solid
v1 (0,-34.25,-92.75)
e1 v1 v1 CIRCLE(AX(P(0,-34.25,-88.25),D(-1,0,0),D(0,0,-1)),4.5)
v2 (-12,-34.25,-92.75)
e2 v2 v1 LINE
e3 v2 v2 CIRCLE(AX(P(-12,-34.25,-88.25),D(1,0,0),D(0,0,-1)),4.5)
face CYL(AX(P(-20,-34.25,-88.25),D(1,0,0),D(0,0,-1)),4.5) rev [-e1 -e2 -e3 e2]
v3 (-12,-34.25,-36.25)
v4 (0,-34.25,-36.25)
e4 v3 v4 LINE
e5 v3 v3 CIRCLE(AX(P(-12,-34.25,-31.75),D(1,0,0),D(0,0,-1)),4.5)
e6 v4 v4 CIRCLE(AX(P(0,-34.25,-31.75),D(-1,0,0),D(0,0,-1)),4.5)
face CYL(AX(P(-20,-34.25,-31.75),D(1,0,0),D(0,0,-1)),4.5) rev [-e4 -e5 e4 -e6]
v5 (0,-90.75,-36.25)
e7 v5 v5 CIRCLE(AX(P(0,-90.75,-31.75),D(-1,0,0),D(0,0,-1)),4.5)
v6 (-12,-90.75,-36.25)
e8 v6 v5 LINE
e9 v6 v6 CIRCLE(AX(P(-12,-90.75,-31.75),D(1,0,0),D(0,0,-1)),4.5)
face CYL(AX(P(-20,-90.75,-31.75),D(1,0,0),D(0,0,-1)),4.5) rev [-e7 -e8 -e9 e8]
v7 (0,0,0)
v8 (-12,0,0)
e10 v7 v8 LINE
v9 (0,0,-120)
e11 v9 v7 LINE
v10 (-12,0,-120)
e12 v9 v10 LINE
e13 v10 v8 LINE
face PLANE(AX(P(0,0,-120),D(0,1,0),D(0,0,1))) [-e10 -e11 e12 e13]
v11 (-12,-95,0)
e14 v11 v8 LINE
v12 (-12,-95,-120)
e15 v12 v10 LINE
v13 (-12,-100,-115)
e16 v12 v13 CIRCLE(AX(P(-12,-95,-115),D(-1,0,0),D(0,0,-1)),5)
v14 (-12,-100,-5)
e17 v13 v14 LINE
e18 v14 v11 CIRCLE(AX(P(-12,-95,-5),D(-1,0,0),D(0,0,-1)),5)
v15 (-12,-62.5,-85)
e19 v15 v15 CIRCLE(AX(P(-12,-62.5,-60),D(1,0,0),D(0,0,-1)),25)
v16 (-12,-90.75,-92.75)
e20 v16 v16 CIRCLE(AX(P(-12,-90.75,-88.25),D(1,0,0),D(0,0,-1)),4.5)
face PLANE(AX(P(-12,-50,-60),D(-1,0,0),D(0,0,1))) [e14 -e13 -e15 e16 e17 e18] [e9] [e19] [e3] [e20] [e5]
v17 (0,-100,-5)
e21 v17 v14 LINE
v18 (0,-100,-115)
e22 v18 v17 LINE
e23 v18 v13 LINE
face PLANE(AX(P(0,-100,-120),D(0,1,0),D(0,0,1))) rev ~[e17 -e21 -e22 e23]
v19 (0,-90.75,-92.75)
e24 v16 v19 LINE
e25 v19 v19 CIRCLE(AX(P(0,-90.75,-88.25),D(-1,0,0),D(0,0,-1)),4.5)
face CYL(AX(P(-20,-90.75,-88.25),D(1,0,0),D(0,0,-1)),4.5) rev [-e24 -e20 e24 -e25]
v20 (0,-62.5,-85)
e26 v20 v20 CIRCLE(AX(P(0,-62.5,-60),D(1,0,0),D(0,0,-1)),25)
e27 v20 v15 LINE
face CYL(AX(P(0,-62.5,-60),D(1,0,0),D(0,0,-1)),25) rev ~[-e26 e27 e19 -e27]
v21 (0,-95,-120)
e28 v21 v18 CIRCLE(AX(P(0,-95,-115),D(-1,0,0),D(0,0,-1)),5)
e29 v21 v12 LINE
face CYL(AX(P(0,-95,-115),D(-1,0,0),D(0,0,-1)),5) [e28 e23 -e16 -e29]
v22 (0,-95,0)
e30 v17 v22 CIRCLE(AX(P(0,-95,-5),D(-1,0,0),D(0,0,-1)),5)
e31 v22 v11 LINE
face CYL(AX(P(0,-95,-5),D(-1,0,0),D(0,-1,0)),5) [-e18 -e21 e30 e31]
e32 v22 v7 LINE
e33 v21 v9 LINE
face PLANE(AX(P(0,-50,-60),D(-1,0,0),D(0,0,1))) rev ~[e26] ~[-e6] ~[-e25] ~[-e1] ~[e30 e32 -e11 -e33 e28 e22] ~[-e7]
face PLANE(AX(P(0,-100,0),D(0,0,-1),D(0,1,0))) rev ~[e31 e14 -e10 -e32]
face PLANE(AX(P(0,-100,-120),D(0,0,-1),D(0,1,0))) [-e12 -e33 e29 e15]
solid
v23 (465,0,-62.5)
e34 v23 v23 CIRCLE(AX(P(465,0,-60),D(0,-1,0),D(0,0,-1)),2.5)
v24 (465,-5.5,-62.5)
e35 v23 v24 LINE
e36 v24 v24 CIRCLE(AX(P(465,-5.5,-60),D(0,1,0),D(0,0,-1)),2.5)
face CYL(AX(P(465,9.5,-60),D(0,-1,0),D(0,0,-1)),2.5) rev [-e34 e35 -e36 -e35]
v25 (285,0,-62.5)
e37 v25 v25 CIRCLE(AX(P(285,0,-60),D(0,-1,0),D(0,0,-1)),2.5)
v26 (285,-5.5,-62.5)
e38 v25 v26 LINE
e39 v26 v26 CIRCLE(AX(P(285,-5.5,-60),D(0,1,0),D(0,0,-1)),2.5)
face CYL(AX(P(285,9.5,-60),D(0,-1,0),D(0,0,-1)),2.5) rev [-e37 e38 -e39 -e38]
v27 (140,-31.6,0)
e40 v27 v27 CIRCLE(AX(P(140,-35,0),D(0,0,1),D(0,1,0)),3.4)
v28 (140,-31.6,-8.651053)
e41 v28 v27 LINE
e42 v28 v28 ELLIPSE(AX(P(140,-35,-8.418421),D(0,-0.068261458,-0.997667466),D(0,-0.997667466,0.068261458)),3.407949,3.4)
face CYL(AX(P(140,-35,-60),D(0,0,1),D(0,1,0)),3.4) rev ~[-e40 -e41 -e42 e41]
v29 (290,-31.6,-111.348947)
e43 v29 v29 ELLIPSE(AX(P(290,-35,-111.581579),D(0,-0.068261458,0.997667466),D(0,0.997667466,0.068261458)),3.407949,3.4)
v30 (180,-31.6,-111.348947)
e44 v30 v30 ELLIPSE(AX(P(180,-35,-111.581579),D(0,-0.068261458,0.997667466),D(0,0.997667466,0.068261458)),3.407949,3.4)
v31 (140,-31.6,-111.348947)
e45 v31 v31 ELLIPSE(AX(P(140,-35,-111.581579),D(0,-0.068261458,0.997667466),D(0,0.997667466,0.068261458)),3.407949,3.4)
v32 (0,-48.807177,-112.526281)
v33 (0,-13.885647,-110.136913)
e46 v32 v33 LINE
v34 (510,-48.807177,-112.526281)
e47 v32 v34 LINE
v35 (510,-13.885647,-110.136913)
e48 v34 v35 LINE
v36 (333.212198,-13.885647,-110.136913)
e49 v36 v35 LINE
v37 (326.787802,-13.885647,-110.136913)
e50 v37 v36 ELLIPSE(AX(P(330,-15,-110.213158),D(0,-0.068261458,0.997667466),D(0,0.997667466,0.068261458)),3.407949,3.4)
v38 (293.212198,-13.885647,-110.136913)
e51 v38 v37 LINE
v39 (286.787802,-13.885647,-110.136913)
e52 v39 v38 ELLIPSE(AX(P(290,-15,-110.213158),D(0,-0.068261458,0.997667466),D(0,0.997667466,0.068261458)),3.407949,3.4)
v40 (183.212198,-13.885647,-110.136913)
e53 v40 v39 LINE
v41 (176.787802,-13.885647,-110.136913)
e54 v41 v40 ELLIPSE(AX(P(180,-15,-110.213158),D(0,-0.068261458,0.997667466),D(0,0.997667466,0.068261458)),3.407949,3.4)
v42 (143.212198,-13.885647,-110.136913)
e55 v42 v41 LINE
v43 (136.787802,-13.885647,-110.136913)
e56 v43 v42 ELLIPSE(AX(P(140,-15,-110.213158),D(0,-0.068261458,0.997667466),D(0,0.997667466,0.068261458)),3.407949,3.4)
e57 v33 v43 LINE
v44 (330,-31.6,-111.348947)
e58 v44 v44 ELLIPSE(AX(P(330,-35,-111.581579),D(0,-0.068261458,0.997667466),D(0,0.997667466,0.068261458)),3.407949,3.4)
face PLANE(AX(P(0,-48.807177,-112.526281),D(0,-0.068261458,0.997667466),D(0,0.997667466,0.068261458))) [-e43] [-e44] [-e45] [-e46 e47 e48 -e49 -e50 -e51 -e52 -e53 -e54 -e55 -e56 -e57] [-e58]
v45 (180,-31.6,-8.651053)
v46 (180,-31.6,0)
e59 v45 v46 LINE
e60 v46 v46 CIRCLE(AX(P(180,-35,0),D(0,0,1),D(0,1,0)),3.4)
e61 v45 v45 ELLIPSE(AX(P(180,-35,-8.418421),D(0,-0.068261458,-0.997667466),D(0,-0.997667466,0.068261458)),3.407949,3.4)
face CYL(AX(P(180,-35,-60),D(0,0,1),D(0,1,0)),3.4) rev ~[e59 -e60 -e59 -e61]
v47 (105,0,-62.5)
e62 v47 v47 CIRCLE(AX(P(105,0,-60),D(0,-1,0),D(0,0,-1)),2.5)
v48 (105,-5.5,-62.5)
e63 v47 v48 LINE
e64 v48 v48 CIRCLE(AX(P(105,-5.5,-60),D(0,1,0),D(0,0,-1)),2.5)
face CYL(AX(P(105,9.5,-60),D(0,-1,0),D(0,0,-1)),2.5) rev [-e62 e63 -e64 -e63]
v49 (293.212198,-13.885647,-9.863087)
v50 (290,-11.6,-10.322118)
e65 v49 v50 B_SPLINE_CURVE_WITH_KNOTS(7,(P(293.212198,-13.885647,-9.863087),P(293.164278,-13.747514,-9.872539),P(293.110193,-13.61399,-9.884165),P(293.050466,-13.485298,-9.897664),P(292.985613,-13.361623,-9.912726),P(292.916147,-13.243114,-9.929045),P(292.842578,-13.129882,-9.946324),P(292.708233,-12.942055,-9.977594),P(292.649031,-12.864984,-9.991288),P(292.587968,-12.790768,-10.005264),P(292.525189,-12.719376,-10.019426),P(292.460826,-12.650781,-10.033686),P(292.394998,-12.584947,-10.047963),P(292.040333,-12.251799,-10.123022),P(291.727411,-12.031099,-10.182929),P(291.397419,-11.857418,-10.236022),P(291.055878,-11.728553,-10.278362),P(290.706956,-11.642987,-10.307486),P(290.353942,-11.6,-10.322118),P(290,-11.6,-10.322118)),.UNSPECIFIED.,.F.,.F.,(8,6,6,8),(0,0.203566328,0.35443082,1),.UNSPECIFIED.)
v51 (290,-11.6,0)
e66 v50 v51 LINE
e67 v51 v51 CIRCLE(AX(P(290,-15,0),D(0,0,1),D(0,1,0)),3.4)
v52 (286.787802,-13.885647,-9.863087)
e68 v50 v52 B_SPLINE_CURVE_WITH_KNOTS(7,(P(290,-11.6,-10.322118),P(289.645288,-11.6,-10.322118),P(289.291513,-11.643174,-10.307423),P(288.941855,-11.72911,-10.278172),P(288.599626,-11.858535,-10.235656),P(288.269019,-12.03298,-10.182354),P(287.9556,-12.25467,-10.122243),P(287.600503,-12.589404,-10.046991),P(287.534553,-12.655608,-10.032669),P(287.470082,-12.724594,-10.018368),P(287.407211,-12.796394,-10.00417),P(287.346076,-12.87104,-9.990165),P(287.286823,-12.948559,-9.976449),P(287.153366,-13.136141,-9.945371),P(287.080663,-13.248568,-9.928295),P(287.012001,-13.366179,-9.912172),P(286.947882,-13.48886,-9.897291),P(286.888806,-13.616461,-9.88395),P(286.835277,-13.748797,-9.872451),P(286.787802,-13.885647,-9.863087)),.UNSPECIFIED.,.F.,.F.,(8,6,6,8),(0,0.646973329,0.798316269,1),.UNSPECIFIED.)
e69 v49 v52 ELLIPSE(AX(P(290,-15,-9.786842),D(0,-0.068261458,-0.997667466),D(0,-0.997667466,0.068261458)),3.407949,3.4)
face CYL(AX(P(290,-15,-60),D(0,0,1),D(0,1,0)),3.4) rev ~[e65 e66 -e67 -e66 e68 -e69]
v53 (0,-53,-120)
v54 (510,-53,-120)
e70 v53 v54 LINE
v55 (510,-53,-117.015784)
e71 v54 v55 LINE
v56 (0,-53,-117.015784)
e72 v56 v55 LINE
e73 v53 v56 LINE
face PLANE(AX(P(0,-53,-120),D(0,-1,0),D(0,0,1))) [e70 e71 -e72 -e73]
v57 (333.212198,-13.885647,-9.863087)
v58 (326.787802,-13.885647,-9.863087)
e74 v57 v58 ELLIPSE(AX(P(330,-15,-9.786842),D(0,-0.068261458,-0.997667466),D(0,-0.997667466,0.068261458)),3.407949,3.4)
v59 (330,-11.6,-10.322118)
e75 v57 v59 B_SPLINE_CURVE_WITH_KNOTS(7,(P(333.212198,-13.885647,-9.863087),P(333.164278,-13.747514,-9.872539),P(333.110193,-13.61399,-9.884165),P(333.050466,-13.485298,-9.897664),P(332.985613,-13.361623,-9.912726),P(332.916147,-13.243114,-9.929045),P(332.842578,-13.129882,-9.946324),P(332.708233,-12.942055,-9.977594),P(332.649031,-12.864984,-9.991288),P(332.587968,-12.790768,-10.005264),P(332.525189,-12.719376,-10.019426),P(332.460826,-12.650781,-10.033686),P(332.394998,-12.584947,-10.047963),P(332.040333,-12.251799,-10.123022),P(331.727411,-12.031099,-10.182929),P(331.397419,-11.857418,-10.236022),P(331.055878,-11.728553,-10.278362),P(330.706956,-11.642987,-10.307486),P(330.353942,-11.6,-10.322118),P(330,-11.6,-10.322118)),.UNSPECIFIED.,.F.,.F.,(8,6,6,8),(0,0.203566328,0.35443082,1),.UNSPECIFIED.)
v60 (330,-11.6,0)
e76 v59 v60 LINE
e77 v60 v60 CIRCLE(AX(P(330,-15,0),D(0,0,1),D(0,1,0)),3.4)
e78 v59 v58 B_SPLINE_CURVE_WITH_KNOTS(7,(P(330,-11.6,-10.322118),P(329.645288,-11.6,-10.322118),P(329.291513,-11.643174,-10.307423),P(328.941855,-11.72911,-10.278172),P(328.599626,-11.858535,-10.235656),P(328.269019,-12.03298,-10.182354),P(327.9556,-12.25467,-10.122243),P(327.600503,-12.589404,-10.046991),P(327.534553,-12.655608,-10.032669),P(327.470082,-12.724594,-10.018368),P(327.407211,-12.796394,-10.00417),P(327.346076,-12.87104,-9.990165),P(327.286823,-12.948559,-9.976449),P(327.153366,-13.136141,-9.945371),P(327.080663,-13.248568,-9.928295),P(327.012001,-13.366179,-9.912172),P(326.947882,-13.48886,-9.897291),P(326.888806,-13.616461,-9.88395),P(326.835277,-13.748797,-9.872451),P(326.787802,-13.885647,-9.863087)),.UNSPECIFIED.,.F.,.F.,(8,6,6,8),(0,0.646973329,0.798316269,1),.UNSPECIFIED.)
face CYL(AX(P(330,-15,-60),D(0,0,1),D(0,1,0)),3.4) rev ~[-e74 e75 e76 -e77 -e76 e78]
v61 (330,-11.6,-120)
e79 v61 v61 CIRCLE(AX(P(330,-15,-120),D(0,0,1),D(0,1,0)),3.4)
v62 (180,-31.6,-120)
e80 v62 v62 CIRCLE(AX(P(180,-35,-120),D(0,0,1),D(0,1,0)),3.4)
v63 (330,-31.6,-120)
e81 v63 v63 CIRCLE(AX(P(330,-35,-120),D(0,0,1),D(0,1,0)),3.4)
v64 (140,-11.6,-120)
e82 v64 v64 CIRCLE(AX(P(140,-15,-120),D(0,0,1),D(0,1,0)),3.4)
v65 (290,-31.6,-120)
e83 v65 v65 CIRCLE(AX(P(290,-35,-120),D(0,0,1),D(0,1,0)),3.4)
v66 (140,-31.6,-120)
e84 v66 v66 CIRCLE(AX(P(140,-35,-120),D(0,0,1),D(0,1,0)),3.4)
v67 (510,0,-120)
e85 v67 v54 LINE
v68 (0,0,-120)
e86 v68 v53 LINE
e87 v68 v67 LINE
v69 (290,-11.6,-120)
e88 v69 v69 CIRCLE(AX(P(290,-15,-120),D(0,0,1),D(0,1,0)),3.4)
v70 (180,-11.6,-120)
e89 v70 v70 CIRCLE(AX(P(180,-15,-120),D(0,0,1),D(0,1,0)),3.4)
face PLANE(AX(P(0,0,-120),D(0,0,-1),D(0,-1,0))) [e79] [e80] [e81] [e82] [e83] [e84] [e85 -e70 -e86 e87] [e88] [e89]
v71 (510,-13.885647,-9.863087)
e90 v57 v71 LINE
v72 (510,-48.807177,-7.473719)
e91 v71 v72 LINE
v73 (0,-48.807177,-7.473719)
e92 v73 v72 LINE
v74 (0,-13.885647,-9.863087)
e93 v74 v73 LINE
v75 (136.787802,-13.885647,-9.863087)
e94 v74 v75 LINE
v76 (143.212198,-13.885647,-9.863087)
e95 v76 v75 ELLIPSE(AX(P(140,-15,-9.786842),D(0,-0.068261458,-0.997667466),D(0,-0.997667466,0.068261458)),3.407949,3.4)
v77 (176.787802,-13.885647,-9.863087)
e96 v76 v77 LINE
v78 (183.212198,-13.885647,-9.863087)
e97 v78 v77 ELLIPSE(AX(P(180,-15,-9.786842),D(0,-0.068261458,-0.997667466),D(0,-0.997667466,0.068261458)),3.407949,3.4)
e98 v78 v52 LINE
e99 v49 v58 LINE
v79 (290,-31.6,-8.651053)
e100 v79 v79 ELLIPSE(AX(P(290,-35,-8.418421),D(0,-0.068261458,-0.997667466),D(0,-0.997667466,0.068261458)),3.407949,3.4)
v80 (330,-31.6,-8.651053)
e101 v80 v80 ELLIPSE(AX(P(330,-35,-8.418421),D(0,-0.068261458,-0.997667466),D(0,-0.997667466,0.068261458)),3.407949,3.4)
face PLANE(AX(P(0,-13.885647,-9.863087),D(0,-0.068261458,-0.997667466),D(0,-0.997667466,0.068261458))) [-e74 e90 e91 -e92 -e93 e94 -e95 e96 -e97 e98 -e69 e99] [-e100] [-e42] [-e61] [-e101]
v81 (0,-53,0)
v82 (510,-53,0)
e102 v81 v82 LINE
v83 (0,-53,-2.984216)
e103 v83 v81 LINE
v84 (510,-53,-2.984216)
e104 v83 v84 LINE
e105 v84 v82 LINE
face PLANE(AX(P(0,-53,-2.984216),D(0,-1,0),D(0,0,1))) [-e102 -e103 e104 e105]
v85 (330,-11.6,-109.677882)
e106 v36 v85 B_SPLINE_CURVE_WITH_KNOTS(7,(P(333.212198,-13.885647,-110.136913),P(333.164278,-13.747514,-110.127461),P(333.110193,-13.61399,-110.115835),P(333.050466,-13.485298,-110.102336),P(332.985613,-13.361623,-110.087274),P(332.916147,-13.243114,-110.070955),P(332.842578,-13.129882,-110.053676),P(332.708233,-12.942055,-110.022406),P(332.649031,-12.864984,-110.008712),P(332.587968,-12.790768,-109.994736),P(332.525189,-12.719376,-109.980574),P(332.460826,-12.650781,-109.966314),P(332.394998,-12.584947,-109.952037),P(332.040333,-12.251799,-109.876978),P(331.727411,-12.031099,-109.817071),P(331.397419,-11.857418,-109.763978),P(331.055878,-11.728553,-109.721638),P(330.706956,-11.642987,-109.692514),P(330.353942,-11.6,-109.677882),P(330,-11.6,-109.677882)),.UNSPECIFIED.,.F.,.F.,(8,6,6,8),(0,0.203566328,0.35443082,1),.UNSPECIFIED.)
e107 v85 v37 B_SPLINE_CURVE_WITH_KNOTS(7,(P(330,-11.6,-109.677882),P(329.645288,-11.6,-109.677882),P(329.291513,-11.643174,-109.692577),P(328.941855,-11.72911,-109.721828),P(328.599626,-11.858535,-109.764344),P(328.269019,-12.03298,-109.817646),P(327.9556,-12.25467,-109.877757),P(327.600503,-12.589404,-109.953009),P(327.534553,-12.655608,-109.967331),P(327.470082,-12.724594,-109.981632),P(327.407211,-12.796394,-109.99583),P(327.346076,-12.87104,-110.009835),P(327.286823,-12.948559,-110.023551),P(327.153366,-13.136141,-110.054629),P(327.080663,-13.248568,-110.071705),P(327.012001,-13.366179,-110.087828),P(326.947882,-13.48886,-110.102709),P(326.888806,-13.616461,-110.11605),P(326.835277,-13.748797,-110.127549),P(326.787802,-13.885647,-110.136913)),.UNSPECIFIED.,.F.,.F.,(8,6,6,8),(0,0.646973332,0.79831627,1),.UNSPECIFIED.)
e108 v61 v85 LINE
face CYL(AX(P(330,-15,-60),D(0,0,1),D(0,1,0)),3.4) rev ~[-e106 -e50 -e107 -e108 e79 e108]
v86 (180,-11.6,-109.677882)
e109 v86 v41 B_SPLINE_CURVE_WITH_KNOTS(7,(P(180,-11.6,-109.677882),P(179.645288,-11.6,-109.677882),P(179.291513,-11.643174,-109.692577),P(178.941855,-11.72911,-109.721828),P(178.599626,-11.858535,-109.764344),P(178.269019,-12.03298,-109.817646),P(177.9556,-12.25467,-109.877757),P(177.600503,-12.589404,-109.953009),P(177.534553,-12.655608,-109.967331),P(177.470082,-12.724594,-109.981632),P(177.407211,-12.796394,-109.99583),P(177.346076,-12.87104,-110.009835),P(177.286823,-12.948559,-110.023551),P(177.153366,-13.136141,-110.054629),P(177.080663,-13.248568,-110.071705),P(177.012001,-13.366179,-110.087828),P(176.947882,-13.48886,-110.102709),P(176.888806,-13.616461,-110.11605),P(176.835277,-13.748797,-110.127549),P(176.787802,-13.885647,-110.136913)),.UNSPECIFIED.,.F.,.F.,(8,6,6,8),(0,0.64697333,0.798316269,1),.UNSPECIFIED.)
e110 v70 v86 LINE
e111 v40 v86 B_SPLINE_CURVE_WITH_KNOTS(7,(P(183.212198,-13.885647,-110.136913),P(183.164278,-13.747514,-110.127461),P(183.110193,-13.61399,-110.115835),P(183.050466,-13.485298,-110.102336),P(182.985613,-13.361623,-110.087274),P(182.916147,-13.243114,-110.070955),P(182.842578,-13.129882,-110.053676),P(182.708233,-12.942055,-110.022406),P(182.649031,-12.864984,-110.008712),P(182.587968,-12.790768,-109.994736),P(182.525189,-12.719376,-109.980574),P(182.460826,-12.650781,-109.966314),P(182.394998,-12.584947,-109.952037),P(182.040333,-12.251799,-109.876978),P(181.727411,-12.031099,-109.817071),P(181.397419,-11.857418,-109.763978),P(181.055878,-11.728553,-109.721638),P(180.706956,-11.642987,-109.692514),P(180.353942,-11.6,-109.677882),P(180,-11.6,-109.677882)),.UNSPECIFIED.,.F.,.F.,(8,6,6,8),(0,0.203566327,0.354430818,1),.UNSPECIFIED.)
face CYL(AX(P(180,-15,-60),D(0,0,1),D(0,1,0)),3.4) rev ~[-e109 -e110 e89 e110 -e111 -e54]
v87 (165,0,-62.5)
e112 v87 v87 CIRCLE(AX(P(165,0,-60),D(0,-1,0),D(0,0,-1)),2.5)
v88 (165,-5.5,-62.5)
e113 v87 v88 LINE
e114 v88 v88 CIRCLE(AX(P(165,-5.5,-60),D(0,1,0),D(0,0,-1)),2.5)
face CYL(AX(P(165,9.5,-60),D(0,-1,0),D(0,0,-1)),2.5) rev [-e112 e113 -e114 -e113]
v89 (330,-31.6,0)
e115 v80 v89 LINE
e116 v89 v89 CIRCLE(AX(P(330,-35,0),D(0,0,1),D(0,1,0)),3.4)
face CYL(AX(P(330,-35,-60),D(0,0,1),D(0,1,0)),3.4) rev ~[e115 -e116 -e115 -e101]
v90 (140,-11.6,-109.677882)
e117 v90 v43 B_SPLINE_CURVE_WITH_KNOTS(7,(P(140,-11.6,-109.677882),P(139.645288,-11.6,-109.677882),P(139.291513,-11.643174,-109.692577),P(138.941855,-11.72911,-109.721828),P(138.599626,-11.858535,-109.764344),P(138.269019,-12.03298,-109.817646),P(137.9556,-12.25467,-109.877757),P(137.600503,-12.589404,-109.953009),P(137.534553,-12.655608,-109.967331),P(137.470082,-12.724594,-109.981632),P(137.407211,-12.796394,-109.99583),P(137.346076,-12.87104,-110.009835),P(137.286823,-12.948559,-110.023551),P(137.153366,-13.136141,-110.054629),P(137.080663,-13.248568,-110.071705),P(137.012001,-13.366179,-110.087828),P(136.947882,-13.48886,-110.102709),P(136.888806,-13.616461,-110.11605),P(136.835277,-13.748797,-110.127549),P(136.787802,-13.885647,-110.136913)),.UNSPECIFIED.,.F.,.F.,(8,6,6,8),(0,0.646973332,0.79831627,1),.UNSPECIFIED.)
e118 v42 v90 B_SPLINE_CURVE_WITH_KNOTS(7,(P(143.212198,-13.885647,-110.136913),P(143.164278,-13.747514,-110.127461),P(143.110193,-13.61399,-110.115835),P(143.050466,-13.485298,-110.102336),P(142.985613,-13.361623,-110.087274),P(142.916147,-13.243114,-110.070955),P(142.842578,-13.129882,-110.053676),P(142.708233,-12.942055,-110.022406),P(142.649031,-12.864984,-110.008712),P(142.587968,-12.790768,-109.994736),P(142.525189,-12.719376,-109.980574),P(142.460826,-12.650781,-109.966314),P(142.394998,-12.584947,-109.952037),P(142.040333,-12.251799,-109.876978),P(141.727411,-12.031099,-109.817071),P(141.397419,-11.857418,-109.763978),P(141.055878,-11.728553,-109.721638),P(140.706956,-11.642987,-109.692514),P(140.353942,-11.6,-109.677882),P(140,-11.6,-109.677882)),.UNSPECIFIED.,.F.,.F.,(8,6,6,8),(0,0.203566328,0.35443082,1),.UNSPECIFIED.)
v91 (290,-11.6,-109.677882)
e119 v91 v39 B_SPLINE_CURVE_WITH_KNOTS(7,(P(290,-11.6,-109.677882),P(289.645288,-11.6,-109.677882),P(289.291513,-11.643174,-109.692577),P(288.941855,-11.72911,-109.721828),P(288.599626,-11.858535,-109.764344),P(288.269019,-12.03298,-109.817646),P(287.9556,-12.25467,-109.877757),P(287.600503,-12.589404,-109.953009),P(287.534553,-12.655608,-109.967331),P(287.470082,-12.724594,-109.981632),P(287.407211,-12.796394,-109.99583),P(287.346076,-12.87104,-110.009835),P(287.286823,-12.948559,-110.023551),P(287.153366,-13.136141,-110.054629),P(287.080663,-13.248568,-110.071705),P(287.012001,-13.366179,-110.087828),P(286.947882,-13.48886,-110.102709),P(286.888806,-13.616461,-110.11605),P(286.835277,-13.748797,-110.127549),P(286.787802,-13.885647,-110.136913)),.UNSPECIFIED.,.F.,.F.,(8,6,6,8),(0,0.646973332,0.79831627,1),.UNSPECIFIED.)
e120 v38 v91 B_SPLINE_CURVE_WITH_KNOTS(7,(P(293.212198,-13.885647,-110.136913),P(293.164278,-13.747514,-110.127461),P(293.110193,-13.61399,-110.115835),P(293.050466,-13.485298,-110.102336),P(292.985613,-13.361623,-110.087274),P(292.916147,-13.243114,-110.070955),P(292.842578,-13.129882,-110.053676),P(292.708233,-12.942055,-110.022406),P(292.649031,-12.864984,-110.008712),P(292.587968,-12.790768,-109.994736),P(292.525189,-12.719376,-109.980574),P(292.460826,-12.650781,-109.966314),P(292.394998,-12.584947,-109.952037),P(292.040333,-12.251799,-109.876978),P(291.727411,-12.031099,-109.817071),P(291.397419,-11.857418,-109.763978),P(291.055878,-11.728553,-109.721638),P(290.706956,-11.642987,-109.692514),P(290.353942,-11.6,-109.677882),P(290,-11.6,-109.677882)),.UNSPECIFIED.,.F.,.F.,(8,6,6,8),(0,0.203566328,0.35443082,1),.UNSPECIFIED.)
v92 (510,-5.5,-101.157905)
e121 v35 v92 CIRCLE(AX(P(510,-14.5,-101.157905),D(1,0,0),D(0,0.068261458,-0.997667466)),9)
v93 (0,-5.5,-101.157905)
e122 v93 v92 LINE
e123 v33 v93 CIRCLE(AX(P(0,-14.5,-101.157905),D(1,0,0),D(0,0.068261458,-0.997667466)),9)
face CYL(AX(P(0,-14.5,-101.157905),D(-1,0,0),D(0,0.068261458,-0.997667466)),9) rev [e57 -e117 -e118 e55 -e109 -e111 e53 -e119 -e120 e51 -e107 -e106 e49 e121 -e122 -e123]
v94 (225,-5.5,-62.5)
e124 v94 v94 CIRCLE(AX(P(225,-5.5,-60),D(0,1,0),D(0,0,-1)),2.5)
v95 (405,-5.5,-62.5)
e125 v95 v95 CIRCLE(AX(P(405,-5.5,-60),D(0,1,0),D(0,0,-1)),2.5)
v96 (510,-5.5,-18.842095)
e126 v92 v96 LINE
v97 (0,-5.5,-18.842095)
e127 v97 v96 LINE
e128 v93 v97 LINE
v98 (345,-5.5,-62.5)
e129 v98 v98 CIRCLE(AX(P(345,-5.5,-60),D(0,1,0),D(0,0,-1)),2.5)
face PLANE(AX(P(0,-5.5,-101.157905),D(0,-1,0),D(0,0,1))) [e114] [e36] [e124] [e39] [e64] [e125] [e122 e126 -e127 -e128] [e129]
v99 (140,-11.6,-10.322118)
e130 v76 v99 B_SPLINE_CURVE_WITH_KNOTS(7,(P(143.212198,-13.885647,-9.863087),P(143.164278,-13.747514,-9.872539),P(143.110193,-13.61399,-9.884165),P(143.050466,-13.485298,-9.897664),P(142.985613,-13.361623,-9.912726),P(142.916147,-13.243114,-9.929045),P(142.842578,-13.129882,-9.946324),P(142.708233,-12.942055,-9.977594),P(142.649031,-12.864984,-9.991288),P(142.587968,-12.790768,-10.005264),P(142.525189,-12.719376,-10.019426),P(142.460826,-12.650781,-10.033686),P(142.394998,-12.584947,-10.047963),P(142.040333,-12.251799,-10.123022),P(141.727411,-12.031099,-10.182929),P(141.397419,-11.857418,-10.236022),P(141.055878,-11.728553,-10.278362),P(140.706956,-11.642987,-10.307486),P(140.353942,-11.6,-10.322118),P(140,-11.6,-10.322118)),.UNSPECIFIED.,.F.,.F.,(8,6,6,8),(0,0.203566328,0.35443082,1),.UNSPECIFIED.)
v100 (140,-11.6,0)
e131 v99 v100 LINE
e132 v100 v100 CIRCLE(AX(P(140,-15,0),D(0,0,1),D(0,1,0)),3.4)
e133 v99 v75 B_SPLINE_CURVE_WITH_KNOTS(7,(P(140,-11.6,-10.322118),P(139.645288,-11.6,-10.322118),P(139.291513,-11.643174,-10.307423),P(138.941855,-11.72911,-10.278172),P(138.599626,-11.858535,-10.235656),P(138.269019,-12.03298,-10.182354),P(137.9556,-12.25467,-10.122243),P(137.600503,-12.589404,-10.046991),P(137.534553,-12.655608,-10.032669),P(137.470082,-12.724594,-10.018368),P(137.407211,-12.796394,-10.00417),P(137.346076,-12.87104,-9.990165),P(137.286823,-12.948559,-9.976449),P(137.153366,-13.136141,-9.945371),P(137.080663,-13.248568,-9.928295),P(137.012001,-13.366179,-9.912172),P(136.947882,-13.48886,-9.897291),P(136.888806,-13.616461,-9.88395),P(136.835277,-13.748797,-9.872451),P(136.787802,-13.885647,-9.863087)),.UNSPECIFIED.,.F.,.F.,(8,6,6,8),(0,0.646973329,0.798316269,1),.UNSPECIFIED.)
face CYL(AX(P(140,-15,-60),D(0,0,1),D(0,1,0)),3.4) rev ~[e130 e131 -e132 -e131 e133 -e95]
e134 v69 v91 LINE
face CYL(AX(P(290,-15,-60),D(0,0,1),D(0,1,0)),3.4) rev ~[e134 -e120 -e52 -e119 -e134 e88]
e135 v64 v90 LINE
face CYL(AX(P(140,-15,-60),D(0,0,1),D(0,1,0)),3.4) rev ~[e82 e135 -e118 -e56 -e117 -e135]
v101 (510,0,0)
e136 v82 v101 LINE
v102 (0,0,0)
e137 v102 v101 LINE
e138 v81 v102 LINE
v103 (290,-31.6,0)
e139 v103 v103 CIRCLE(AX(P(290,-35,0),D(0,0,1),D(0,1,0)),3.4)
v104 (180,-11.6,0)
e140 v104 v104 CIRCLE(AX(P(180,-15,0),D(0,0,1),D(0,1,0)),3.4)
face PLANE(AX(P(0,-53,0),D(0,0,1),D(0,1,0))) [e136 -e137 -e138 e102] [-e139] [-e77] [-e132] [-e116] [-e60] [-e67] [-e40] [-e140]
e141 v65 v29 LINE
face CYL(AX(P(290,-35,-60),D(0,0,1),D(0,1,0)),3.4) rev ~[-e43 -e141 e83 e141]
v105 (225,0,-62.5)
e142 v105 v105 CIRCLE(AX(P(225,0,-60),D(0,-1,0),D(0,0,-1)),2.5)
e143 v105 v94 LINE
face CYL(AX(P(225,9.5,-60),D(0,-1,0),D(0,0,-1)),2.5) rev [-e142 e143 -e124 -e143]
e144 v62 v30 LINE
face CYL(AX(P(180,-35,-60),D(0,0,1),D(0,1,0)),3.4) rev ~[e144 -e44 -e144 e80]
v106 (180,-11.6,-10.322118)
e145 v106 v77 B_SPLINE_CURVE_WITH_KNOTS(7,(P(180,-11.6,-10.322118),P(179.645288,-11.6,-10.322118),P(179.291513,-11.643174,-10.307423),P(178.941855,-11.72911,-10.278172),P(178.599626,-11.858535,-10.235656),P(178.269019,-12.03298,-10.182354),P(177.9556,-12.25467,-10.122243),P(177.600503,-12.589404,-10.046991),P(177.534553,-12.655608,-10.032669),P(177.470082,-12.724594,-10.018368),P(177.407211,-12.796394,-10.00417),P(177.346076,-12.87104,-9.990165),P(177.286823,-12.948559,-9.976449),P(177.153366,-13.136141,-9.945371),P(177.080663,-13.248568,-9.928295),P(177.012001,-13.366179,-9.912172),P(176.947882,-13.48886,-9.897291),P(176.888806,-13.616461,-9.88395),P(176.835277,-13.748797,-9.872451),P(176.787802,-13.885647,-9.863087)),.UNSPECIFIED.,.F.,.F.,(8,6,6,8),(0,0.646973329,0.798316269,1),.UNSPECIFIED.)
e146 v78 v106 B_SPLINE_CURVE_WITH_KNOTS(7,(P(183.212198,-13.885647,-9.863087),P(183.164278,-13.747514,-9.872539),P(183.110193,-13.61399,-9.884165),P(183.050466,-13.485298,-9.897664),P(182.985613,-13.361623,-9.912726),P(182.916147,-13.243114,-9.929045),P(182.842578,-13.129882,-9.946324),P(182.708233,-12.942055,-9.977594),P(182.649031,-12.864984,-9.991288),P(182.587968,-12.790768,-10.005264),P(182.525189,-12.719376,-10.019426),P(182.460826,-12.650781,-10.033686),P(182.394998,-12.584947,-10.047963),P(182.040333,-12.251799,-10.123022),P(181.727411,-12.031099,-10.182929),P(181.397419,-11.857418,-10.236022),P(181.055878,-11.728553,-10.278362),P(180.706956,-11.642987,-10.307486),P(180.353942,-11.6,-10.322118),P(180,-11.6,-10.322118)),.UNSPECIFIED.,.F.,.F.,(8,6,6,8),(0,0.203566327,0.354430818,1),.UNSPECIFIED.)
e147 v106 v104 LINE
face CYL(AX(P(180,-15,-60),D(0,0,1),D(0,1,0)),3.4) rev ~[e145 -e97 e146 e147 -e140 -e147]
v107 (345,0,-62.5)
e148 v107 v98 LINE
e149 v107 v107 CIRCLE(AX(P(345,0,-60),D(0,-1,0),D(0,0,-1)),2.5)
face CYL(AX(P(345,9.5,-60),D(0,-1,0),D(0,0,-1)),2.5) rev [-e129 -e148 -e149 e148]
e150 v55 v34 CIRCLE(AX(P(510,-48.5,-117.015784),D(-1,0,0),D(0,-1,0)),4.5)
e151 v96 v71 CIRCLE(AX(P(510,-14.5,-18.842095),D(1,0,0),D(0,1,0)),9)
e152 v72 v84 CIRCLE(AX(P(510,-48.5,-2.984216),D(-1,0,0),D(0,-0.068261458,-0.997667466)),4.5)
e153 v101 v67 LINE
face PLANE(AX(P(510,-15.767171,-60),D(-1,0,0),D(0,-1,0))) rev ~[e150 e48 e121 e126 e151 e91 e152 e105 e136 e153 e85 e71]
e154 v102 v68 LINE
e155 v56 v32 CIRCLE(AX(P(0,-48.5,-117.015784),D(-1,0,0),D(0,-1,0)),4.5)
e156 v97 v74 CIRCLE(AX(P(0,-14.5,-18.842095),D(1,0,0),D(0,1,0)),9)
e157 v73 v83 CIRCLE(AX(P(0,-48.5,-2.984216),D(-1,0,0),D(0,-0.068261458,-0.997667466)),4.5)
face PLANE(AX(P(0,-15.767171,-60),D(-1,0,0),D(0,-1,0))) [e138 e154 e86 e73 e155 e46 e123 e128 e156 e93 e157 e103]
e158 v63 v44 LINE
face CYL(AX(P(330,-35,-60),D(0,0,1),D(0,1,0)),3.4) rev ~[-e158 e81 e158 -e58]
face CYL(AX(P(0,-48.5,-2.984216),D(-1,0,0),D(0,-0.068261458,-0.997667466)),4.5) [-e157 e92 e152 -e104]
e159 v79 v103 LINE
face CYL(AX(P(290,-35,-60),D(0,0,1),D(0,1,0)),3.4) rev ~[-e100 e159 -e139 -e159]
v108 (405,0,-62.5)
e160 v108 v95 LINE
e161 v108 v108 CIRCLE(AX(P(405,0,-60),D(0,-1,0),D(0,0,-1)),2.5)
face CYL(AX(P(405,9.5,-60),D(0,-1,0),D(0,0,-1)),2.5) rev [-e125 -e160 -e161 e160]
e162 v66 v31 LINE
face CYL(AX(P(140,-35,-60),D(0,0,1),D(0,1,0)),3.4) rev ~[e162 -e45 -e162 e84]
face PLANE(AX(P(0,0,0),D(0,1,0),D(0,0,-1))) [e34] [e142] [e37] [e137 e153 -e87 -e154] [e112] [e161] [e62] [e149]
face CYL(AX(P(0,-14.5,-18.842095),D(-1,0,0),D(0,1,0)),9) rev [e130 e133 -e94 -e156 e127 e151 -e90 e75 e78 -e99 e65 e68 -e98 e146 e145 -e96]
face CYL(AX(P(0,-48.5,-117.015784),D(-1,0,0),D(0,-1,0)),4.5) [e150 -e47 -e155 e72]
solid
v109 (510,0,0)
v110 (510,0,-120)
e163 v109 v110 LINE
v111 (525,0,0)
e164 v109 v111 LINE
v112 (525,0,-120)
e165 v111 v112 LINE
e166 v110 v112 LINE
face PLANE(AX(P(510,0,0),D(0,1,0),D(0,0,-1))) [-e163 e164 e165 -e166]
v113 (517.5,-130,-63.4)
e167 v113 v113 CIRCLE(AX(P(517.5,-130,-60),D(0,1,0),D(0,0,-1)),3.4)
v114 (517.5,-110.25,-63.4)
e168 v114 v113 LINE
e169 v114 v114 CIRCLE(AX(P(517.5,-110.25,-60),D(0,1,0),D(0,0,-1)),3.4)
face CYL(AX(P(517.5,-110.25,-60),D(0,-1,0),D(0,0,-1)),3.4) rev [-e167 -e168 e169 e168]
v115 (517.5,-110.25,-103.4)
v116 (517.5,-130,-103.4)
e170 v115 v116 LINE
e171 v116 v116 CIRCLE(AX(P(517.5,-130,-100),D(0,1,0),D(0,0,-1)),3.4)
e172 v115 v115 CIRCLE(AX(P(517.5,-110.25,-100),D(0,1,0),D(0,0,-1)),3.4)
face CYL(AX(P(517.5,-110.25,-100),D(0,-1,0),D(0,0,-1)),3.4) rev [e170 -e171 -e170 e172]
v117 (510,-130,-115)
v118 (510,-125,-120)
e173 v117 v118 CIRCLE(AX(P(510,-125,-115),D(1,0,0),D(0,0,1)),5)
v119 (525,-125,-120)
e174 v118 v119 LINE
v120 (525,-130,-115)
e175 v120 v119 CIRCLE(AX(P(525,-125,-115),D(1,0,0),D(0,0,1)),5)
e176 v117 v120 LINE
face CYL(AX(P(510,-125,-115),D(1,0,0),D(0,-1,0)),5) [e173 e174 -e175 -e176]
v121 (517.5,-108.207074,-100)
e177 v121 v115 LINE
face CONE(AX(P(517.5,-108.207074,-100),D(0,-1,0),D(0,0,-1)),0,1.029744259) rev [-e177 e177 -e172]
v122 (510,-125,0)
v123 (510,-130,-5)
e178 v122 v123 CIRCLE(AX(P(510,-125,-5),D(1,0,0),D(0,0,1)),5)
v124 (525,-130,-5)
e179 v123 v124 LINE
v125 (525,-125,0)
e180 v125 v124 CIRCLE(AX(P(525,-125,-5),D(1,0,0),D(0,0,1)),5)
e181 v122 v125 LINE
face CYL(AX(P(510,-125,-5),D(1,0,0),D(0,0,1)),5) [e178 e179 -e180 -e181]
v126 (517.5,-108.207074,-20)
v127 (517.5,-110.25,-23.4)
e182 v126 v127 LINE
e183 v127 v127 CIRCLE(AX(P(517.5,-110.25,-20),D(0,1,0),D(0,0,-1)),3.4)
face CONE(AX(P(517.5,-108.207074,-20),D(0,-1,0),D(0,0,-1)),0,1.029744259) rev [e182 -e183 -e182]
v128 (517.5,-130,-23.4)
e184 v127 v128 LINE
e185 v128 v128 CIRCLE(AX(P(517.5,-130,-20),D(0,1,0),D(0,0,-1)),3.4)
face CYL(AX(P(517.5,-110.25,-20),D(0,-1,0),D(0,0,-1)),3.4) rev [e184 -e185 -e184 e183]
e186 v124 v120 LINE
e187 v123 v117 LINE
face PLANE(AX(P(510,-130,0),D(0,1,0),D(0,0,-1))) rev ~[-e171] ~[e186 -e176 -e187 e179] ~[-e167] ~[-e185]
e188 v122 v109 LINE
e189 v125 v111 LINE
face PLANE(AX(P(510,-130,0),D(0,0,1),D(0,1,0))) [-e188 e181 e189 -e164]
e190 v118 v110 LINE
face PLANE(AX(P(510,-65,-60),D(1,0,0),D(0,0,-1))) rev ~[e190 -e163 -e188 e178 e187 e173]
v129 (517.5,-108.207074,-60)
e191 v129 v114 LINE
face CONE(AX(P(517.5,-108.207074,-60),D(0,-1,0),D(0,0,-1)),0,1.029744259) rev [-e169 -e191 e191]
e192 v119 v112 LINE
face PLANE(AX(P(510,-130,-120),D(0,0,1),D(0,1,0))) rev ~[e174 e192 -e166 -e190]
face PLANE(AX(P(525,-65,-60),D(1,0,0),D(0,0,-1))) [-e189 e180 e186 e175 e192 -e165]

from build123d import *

# Parameters (mm, degrees)
MEMBER_1_DEPTH                   = 510
SKETCH_5_W                       = 120
SKETCH_5_H                       = 100
EXTRUDE_1_DEPTH                  = 12
SKETCH_6_W                       = 120
SKETCH_6_H                       = 130
EXTRUDE_2_DEPTH                  = 15
FILLET_1_R                       = 5
FILLET_2_R                       = 5
HOLE_WIZARD_M6_1_AT_2_COUNT      = 2
HOLE_WIZARD_M6_1_AT_2_PITCH      = 60
HOLE_WIZARD_M6_1_AT_3_COUNT      = 2
HOLE_WIZARD_M6_1_AT_3_PITCH      = 120
HOLE_WIZARD_M6_1_AT_4_COUNT      = 2
HOLE_WIZARD_M6_1_AT_4_PITCH      = 180
HOLE_WIZARD_M6_1_AT_5_COUNT      = 2
HOLE_WIZARD_M6_1_AT_5_PITCH      = 240
HOLE_WIZARD_M6_1_AT_6_COUNT      = 2
HOLE_WIZARD_M6_1_AT_6_PITCH      = 300
HOLE_WIZARD_M6_1_AT_7_COUNT      = 2
HOLE_WIZARD_M6_1_AT_7_PITCH      = 360
HOLE_WIZARD_M8_1_AT_2_COUNT      = 2
HOLE_WIZARD_M8_1_AT_2_PITCH      = 80
HOLE_WIZARD_M8_1_AT_3_COUNT      = 2
HOLE_WIZARD_M8_1_AT_3_PITCH      = 40
SKETCH_11_W                      = 3.4
SKETCH_11_H                      = 120
HOLE_WIZARD_M8_2_AT_2_COUNT      = 2
HOLE_WIZARD_M8_2_AT_2_PITCH      = 20
HOLE_WIZARD_M8_2_AT_3_COUNT      = 2
HOLE_WIZARD_M8_2_AT_3_PITCH      = 44.72135955
HOLE_WIZARD_M8_2_AT_4_COUNT      = 2
HOLE_WIZARD_M8_2_AT_4_PITCH      = 40
HOLE_WIZARD_9_0_9_1_AT_2_COUNT   = 2
HOLE_WIZARD_9_0_9_1_AT_2_PITCH   = 56.5
HOLE_WIZARD_9_0_9_1_AT_3_COUNT   = 2
HOLE_WIZARD_9_0_9_1_AT_3_PITCH   = 79.903066274
HOLE_WIZARD_9_0_9_1_AT_4_COUNT   = 2
HOLE_WIZARD_9_0_9_1_AT_4_PITCH   = 56.5
SKETCH_15_R                      = 25
CUT_EXTRUDE_1_DEPTH              = 20
PATTERN_LINEAR_1_COUNT           = 2
PATTERN_LINEAR_1_PITCH           = 150
PATTERN_LINEAR_1_COPY_1_SKETCH_W = 3.4
PATTERN_LINEAR_1_COPY_1_SKETCH_H = 120
PATTERN_LINEAR_1_COPY_2_SKETCH_W = 3.4
PATTERN_LINEAR_1_COPY_2_SKETCH_H = 120
PATTERN_LINEAR_1_COPY_3_SKETCH_W = 3.4
PATTERN_LINEAR_1_COPY_3_SKETCH_H = 120


with BuildPart() as part:
    # Sketch1 → Member 1 (new body)
    with BuildSketch(Plane.YZ):
        with BuildLine():
            Line((0, 0), (0, -120))
            Line((0, -120), (-53, -120))
            Line((-53, -120), (-53, -117.0157841))
            ThreePointArc((-53, -117.0157841), (-51.788791155, -113.944326346), (-48.807176562, -112.526280502))
            Line((-48.807176562, -112.526280502), (-13.885646876, -110.136912681))
            ThreePointArc((-13.885646876, -110.136912681), (-7.922417689, -107.300820993), (-5.5, -101.157905484))
            Line((-5.5, -101.157905484), (-5.5, -18.842094516))
            ThreePointArc((-5.5, -18.842094516), (-7.922417689, -12.699179007), (-13.885646876, -9.863087319))
            Line((-13.885646876, -9.863087319), (-48.807176562, -7.473719498))
            ThreePointArc((-48.807176562, -7.473719498), (-51.788791155, -6.055673654), (-53, -2.9842159))
            Line((-53, -2.9842159), (-53, 0))
            Line((-53, 0), (0, 0))
        make_face()
    extrude(amount=MEMBER_1_DEPTH)

    # 草图7 → M6 螺纹孔1 (revolve, cut)
    with BuildSketch(Plane(origin=(105, -5.5, -60), x_dir=(0, 0, -1), z_dir=(1, 0, 0))):
        Polygon((0, 0), (0, 16.502151548), (2.5, 15), (2.5, 0), align=None)
    hole_wizard_m6_1 = revolve(axis=Axis((105, -11.85, -60), (0, 1, 0)), mode=Mode.SUBTRACT)

    # M6 螺纹孔1 at 2: M6 螺纹孔1 ×2
    with Locations(*[(i * HOLE_WIZARD_M6_1_AT_2_PITCH, 0, 0) for i in range(1, HOLE_WIZARD_M6_1_AT_2_COUNT)]):
        add(hole_wizard_m6_1, mode=Mode.SUBTRACT)

    # M6 螺纹孔1 at 3: M6 螺纹孔1 ×2
    with Locations(*[(i * HOLE_WIZARD_M6_1_AT_3_PITCH, 0, 0) for i in range(1, HOLE_WIZARD_M6_1_AT_3_COUNT)]):
        add(hole_wizard_m6_1, mode=Mode.SUBTRACT)

    # M6 螺纹孔1 at 4: M6 螺纹孔1 ×2
    with Locations(*[(i * HOLE_WIZARD_M6_1_AT_4_PITCH, 0, 0) for i in range(1, HOLE_WIZARD_M6_1_AT_4_COUNT)]):
        add(hole_wizard_m6_1, mode=Mode.SUBTRACT)

    # M6 螺纹孔1 at 5: M6 螺纹孔1 ×2
    with Locations(*[(i * HOLE_WIZARD_M6_1_AT_5_PITCH, 0, 0) for i in range(1, HOLE_WIZARD_M6_1_AT_5_COUNT)]):
        add(hole_wizard_m6_1, mode=Mode.SUBTRACT)

    # M6 螺纹孔1 at 6: M6 螺纹孔1 ×2
    with Locations(*[(i * HOLE_WIZARD_M6_1_AT_6_PITCH, 0, 0) for i in range(1, HOLE_WIZARD_M6_1_AT_6_COUNT)]):
        add(hole_wizard_m6_1, mode=Mode.SUBTRACT)

    # M6 螺纹孔1 at 7: M6 螺纹孔1 ×2
    with Locations(*[(i * HOLE_WIZARD_M6_1_AT_7_PITCH, 0, 0) for i in range(1, HOLE_WIZARD_M6_1_AT_7_COUNT)]):
        add(hole_wizard_m6_1, mode=Mode.SUBTRACT)

    # 草图11 → M8 螺纹孔2 (revolve, cut)
    with BuildSketch(Plane(origin=(140, -15, -120), x_dir=(0, 1, 0), z_dir=(1, 0, 0))):
        with Locations((1.7, 60)):
            Rectangle(SKETCH_11_W, SKETCH_11_H)
    hole_wizard_m8_2 = revolve(axis=Axis((140, -15, -126.35), (0, 0, 1)), mode=Mode.SUBTRACT)

    # M8 螺纹孔2 at 2: M8 螺纹孔2 ×2
    with Locations(*[(0, -i * HOLE_WIZARD_M8_2_AT_2_PITCH, 0) for i in range(1, HOLE_WIZARD_M8_2_AT_2_COUNT)]):
        add(hole_wizard_m8_2, mode=Mode.SUBTRACT)

    # M8 螺纹孔2 at 3: M8 螺纹孔2 ×2
    with Locations(*[Vector(0.8944271909999159, -0.447213595499958, 0) * (i * HOLE_WIZARD_M8_2_AT_3_PITCH) for i in range(1, HOLE_WIZARD_M8_2_AT_3_COUNT)]):
        add(hole_wizard_m8_2, mode=Mode.SUBTRACT)

    # M8 螺纹孔2 at 4: M8 螺纹孔2 ×2
    with Locations(*[(i * HOLE_WIZARD_M8_2_AT_4_PITCH, 0, 0) for i in range(1, HOLE_WIZARD_M8_2_AT_4_COUNT)]):
        add(hole_wizard_m8_2, mode=Mode.SUBTRACT)

    # 阵列(线性)1: M8 螺纹孔2 ×2
    with Locations(*[(i * PATTERN_LINEAR_1_PITCH, 0, 0) for i in range(1, PATTERN_LINEAR_1_COUNT)]):
        add(hole_wizard_m8_2, mode=Mode.SUBTRACT)

    # 阵列(线性)1 copy 1 sketch → 阵列(线性)1 copy 1 (revolve, cut)
    with BuildSketch(Plane(origin=(290, -35, -120), x_dir=(0, 1, 0), z_dir=(1, 0, 0))):
        with Locations((1.7, 60)):
            Rectangle(PATTERN_LINEAR_1_COPY_1_SKETCH_W, PATTERN_LINEAR_1_COPY_1_SKETCH_H)
    revolve(axis=Axis((290, -35, -126.35), (0, 0, 1)), mode=Mode.SUBTRACT)

    # 阵列(线性)1 copy 2 sketch → 阵列(线性)1 copy 2 (revolve, cut)
    with BuildSketch(Plane(origin=(330, -35, -120), x_dir=(0, 1, 0), z_dir=(1, 0, 0))):
        with Locations((1.7, 60)):
            Rectangle(PATTERN_LINEAR_1_COPY_2_SKETCH_W, PATTERN_LINEAR_1_COPY_2_SKETCH_H)
    revolve(axis=Axis((330, -35, -126.35), (0, 0, 1)), mode=Mode.SUBTRACT)

    # 阵列(线性)1 copy 3 sketch → 阵列(线性)1 copy 3 (revolve, cut)
    with BuildSketch(Plane(origin=(330, -15, -120), x_dir=(0, 1, 0), z_dir=(1, 0, 0))):
        with Locations((1.7, 60)):
            Rectangle(PATTERN_LINEAR_1_COPY_3_SKETCH_W, PATTERN_LINEAR_1_COPY_3_SKETCH_H)
    revolve(axis=Axis((330, -15, -126.35), (0, 0, 1)), mode=Mode.SUBTRACT)


with BuildPart() as body_2:
    # 草图5 → 凸台-拉伸1 (new body)
    with BuildSketch(Plane.ZY):
        with Locations((-60, -50)):
            Rectangle(SKETCH_5_W, SKETCH_5_H)
    extrude(amount=EXTRUDE_1_DEPTH)

    # 圆角1
    fillet_1_edges = [body_2.edges().sort_by_distance(p)[0] for p in [
        (-6, -100, 0),
        (-6, -100, -120),
    ]]
    fillet(fillet_1_edges, radius=FILLET_1_R)

    # 草图13 → Ø9.0 (9) 直径孔1 (revolve, cut)
    with BuildSketch(Plane(origin=(0, -90.75, -31.75), x_dir=(0, 0, -1), z_dir=(0, 1, 0))):
        Polygon((0, 0), (0, 22.703872786), (4.5, 20), (4.5, 0), align=None)
    hole_wizard_9_0_9_1 = revolve(axis=Axis((6.35, -90.75, -31.75), (-1, 0, 0)), mode=Mode.SUBTRACT)

    # Ø9.0 (9) 直径孔1 at 2: Ø9.0 (9) 直径孔1 ×2
    with Locations(*[(0, i * HOLE_WIZARD_9_0_9_1_AT_2_PITCH, 0) for i in range(1, HOLE_WIZARD_9_0_9_1_AT_2_COUNT)]):
        add(hole_wizard_9_0_9_1, mode=Mode.SUBTRACT)

    # Ø9.0 (9) 直径孔1 at 3: Ø9.0 (9) 直径孔1 ×2
    with Locations(*[Vector(0, 0.7071067811865475, -0.7071067811865476) * (i * HOLE_WIZARD_9_0_9_1_AT_3_PITCH) for i in range(1, HOLE_WIZARD_9_0_9_1_AT_3_COUNT)]):
        add(hole_wizard_9_0_9_1, mode=Mode.SUBTRACT)

    # Ø9.0 (9) 直径孔1 at 4: Ø9.0 (9) 直径孔1 ×2
    with Locations(*[(0, 0, -i * HOLE_WIZARD_9_0_9_1_AT_4_PITCH) for i in range(1, HOLE_WIZARD_9_0_9_1_AT_4_COUNT)]):
        add(hole_wizard_9_0_9_1, mode=Mode.SUBTRACT)

    # 草图15 → 切除-拉伸1 (cut)
    with BuildSketch(Plane(origin=(0, 0, 0), x_dir=(0, 0, -1), z_dir=(1, 0, 0))):
        with Locations((60, -62.5)):
            Circle(SKETCH_15_R)
    extrude(amount=-CUT_EXTRUDE_1_DEPTH, mode=Mode.SUBTRACT)


with BuildPart() as body_3:
    # 草图6 → 凸台-拉伸2 (new body)
    with BuildSketch(Plane(origin=(510, 0, 0), x_dir=(0, 0, -1), z_dir=(1, 0, 0))):
        with Locations((60, -65)):
            Rectangle(SKETCH_6_W, SKETCH_6_H)
    extrude(amount=EXTRUDE_2_DEPTH)

    # 圆角2
    fillet_2_edges = [body_3.edges().sort_by_distance(p)[0] for p in [
        (517.5, -130, -120),
        (517.5, -130, 0),
    ]]
    fillet(fillet_2_edges, radius=FILLET_2_R)

    # 草图9 → M8 螺纹孔1 (revolve, cut)
    with BuildSketch(Plane(origin=(517.5, -130, -100), x_dir=(0, 0, -1), z_dir=(1, 0, 0))):
        Polygon((0, 0), (0, 21.792926105), (3.4, 19.75), (3.4, 0), align=None)
    hole_wizard_m8_1 = revolve(axis=Axis((517.5, -136.35, -100), (0, 1, 0)), mode=Mode.SUBTRACT)

    # M8 螺纹孔1 at 2: M8 螺纹孔1 ×2
    with Locations(*[(0, 0, i * HOLE_WIZARD_M8_1_AT_2_PITCH) for i in range(1, HOLE_WIZARD_M8_1_AT_2_COUNT)]):
        add(hole_wizard_m8_1, mode=Mode.SUBTRACT)

    # M8 螺纹孔1 at 3: M8 螺纹孔1 ×2
    with Locations(*[(0, 0, i * HOLE_WIZARD_M8_1_AT_3_PITCH) for i in range(1, HOLE_WIZARD_M8_1_AT_3_COUNT)]):
        add(hole_wizard_m8_1, mode=Mode.SUBTRACT)


solid = Compound([part.part, body_2.part, body_3.part])
